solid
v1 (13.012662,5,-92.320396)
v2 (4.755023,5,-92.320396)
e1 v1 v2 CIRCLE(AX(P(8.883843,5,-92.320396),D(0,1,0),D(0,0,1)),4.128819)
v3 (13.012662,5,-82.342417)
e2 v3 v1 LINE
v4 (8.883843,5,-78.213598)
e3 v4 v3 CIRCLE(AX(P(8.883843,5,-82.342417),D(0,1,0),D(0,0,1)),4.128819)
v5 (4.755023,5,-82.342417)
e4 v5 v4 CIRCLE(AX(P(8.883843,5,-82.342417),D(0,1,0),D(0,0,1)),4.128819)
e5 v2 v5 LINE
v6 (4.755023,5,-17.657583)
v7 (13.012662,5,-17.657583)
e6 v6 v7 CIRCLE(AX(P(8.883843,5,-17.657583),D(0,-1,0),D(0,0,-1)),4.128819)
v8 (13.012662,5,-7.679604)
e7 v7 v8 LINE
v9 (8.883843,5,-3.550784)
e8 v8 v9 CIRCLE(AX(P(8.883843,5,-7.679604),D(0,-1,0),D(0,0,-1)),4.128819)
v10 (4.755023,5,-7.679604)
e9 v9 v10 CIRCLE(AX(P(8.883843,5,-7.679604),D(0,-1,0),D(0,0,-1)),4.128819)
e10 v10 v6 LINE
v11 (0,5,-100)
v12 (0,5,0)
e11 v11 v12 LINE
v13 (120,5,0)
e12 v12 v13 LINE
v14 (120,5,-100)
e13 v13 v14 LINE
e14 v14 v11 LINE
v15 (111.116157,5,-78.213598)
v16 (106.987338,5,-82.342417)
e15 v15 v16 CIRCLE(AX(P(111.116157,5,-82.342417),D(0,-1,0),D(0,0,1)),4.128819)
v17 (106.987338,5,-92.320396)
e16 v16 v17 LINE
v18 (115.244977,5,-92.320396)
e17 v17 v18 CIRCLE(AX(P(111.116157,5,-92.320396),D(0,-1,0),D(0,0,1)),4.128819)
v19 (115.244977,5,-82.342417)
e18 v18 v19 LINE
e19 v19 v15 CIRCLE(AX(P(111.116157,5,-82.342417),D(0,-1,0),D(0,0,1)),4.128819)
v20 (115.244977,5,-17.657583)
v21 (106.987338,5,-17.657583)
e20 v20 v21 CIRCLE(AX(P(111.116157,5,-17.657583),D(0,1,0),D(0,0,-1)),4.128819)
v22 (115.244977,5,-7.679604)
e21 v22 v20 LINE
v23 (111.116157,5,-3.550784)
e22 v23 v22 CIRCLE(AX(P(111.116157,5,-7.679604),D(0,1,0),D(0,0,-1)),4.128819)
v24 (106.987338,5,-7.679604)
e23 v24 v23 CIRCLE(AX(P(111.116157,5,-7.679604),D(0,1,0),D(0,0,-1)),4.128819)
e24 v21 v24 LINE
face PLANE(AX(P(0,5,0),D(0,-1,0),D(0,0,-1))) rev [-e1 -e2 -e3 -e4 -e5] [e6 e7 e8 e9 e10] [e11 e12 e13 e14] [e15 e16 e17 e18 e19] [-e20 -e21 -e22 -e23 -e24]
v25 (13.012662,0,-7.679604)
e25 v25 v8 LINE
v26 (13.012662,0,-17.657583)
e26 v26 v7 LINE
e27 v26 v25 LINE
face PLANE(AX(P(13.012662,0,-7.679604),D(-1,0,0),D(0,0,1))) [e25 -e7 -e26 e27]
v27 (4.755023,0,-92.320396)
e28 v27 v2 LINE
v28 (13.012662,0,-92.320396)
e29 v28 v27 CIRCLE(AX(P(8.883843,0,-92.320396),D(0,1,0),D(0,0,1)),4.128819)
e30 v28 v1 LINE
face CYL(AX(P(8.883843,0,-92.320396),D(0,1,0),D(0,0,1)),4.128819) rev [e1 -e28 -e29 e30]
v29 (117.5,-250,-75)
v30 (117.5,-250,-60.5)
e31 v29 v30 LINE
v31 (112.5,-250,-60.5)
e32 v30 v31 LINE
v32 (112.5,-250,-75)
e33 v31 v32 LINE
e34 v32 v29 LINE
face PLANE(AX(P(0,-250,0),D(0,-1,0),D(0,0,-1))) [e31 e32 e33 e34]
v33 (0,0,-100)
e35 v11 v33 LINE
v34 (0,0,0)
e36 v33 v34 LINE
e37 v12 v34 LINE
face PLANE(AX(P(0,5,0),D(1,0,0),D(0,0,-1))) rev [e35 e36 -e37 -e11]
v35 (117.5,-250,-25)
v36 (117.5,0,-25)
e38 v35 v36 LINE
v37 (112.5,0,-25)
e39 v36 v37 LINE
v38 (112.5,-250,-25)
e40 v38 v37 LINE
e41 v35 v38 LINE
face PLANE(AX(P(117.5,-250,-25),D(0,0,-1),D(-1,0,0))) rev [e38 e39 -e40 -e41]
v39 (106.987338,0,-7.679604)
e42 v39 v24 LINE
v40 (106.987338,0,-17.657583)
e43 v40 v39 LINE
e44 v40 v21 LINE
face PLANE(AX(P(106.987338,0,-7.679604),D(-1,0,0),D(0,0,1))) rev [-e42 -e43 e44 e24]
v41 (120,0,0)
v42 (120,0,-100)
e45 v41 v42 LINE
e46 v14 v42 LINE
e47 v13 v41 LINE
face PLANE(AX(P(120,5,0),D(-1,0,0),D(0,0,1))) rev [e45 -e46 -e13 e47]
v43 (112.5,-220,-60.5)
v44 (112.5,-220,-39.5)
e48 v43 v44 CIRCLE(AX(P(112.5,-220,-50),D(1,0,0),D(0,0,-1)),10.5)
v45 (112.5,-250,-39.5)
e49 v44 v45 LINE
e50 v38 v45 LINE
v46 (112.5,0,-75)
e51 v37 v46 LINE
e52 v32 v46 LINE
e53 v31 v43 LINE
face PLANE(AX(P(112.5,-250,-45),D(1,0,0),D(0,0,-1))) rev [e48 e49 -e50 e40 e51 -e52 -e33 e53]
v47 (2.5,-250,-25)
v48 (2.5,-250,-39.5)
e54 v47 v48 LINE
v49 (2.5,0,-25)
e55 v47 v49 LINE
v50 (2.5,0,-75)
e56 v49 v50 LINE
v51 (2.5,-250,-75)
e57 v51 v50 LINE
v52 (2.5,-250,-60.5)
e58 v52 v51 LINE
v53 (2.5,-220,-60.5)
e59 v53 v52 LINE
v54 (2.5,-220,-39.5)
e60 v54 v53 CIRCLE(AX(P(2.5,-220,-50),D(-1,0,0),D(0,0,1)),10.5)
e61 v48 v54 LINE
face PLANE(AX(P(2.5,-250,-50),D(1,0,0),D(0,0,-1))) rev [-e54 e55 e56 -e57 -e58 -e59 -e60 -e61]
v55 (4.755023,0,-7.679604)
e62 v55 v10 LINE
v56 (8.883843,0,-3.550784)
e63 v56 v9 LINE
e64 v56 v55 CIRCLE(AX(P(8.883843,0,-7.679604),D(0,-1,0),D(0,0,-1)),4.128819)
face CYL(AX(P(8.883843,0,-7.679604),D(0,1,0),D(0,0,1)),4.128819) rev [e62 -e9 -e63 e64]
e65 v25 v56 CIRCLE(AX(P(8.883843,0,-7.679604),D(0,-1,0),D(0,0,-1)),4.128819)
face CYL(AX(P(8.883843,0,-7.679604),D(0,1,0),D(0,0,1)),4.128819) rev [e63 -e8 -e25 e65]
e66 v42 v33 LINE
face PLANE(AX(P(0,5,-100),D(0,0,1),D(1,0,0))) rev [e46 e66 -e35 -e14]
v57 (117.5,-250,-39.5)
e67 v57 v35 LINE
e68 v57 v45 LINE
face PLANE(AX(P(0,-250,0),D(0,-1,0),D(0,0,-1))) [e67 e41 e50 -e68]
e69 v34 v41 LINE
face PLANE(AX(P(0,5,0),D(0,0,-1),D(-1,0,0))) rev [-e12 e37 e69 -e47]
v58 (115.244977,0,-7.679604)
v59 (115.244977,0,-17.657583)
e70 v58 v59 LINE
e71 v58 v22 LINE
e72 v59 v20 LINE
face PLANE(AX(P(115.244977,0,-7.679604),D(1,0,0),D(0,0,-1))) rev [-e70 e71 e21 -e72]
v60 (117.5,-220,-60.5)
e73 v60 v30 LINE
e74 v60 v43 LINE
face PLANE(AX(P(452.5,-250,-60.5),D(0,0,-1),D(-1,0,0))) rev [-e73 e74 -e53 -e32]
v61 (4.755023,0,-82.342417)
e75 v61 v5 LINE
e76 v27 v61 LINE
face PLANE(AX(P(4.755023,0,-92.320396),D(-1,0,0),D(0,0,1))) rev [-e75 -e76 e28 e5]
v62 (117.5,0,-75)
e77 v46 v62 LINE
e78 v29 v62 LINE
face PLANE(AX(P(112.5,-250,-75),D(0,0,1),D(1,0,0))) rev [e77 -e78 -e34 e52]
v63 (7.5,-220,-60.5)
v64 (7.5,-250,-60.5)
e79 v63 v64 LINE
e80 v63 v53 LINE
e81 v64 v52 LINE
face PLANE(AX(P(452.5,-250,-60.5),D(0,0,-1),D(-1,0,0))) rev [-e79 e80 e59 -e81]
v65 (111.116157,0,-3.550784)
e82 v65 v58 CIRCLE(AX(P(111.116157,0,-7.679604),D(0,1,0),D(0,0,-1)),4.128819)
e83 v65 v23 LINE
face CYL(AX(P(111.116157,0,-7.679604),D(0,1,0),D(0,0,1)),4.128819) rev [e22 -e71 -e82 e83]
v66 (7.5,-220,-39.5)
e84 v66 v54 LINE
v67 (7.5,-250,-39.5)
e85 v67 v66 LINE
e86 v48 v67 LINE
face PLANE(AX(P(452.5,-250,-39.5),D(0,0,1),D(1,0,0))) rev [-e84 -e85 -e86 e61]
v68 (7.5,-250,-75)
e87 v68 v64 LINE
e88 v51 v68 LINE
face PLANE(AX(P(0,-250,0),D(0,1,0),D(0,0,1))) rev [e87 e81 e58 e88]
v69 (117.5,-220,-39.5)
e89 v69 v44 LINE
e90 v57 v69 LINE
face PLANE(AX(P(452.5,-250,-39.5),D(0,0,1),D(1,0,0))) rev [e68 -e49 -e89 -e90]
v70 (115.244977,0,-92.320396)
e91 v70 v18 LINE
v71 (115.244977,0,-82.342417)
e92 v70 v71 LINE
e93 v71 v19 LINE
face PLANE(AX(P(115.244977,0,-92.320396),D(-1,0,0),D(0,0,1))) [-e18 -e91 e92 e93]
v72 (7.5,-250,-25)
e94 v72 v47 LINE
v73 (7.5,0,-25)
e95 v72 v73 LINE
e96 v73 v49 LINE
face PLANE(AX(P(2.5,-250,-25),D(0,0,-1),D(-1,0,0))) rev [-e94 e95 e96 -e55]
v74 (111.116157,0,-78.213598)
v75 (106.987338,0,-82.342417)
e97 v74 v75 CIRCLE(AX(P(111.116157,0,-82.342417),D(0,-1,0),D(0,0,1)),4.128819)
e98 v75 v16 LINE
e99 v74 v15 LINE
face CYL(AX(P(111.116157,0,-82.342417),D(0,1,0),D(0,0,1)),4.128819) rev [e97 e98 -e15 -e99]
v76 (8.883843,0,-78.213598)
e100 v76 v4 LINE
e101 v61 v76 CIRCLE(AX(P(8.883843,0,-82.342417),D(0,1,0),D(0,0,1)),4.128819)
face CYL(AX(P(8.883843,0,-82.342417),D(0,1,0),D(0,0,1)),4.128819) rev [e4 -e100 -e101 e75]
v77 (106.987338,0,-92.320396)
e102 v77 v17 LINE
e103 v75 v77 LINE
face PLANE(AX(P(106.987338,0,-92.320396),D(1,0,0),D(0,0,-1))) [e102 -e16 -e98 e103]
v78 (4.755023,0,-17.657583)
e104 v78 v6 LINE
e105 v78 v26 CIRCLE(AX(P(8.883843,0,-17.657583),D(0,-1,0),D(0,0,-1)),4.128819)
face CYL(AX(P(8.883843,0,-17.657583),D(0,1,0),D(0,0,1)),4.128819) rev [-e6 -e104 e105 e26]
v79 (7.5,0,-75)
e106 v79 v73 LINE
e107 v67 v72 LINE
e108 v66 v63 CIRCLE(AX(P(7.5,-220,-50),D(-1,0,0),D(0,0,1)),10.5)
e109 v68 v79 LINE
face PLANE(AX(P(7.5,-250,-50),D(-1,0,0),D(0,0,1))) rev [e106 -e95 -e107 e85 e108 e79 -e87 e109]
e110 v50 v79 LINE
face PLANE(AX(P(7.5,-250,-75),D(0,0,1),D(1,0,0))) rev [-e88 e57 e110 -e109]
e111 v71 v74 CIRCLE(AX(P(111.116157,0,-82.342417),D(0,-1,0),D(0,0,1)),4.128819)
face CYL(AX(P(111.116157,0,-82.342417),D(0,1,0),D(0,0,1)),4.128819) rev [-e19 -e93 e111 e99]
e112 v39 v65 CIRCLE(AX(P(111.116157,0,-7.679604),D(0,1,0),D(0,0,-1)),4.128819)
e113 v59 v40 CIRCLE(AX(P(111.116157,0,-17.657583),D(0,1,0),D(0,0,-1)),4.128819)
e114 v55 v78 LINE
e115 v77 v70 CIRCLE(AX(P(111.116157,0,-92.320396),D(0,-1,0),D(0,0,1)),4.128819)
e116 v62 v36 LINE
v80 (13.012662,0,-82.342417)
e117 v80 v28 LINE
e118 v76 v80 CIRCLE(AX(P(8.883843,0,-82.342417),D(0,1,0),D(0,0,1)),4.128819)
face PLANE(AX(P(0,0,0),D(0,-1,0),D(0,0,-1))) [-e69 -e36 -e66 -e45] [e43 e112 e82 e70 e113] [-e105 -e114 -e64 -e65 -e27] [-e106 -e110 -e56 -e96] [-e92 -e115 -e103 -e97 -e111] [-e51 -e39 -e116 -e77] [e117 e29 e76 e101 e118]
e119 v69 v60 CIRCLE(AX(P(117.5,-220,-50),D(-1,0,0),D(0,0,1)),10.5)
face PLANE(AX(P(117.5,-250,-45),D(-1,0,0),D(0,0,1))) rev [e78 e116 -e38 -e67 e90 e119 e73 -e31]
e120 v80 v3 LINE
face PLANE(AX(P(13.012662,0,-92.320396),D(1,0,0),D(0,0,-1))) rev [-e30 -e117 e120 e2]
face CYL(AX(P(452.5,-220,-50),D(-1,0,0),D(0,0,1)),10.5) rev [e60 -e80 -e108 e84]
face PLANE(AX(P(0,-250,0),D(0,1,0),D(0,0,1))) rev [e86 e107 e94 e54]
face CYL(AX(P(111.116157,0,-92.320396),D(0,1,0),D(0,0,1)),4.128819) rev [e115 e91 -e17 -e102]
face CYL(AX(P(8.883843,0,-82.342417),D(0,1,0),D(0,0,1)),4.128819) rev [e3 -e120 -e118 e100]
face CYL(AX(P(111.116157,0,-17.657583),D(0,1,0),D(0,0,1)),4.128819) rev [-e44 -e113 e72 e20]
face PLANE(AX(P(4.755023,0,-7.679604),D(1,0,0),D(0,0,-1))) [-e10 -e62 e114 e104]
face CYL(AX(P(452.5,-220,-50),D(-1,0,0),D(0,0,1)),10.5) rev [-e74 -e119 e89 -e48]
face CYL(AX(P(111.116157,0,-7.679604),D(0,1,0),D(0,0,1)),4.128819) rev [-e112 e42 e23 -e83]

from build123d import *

# Parameters (mm, degrees)
SKETCH1_W            = 120
SKETCH1_H            = 100
BOSS_EXTRUDE1_DEPTH  = 5
CUT_EXTRUDE1_DEPTH   = 157.284996081
MIRROR2_COPY_1_DEPTH = 157.284996081
BOSS_EXTRUDE2_DEPTH  = 250
CUT_EXTRUDE2_DEPTH   = 450


with BuildPart() as part:
    # Sketch1 → Boss-Extrude1 (new body)
    with BuildSketch(Plane(origin=(0, 0, 0), x_dir=(1, 0, 0), z_dir=(0, 1, 0))):
        with Locations((60, 50)):
            Rectangle(SKETCH1_W, SKETCH1_H)
    extrude(amount=BOSS_EXTRUDE1_DEPTH)

    # Sketch2 → Cut-Extrude1 (cut, through all)
    with BuildSketch(Plane(origin=(0, 5, 0), x_dir=(1, 0, 0), z_dir=(0, 1, 0))):
        with BuildLine():
            Line((13.012661712, 92.320396367), (13.012661712, 82.342416735))
            ThreePointArc((13.012661712, 82.342416735), (8.883842554, 78.213597578), (4.755023397, 82.342416735))
            Line((4.755023397, 82.342416735), (4.755023397, 92.320396367))
            ThreePointArc((4.755023397, 92.320396367), (8.883842554, 96.449215524), (13.012661712, 92.320396367))
        make_face()
    cut_extrude1 = extrude(amount=-CUT_EXTRUDE1_DEPTH, mode=Mode.SUBTRACT)

    # Mirror1: Cut-Extrude1 across plane
    add(cut_extrude1.mirror(Plane.ZY.offset(-60)), mode=Mode.SUBTRACT)

    # Mirror2: Cut-Extrude1 across plane
    add(cut_extrude1.mirror(Plane.XY.offset(-50)), mode=Mode.SUBTRACT)

    # Mirror2 copy 1 sketch → Mirror2 copy 1 (cut, through all)
    with BuildSketch(Plane(origin=(120, 5, -100), x_dir=(-1, 0, 0), z_dir=(0, 1, 0))):
        with BuildLine():
            Line((13.012661712, 92.320396367), (13.012661712, 82.342416735))
            ThreePointArc((13.012661712, 82.342416735), (8.883842554, 78.213597578), (4.755023397, 82.342416735))
            Line((4.755023397, 82.342416735), (4.755023397, 92.320396367))
            ThreePointArc((4.755023397, 92.320396367), (8.883842554, 96.449215524), (13.012661712, 92.320396367))
        make_face()
    extrude(amount=-MIRROR2_COPY_1_DEPTH, mode=Mode.SUBTRACT)

    # Sketch4 → Boss-Extrude2 (add)
    with BuildSketch(Plane.XZ):
        Polygon((2.5, -50), (2.5, -75), (7.5, -75), (7.5, -50), (7.5, -25), (2.5, -25), align=None)
        Polygon((112.5, -75), (117.5, -75), (117.5, -45), (117.5, -25), (112.5, -25), (112.5, -45), align=None)
    extrude(amount=BOSS_EXTRUDE2_DEPTH)

    # Sketch5 → Cut-Extrude2 (cut)
    with BuildSketch(Plane.ZY.offset(-2.5)):
        with BuildLine():
            Line((-60.5, -250), (-60.5, -220))
            ThreePointArc((-60.5, -220), (-50, -209.5), (-39.5, -220))
            Line((-39.5, -220), (-39.5, -250))
            ThreePointArc((-39.5, -250), (-50, -260.5), (-60.5, -250))
        make_face()
    extrude(amount=-CUT_EXTRUDE2_DEPTH, mode=Mode.SUBTRACT)


solid = part.part
